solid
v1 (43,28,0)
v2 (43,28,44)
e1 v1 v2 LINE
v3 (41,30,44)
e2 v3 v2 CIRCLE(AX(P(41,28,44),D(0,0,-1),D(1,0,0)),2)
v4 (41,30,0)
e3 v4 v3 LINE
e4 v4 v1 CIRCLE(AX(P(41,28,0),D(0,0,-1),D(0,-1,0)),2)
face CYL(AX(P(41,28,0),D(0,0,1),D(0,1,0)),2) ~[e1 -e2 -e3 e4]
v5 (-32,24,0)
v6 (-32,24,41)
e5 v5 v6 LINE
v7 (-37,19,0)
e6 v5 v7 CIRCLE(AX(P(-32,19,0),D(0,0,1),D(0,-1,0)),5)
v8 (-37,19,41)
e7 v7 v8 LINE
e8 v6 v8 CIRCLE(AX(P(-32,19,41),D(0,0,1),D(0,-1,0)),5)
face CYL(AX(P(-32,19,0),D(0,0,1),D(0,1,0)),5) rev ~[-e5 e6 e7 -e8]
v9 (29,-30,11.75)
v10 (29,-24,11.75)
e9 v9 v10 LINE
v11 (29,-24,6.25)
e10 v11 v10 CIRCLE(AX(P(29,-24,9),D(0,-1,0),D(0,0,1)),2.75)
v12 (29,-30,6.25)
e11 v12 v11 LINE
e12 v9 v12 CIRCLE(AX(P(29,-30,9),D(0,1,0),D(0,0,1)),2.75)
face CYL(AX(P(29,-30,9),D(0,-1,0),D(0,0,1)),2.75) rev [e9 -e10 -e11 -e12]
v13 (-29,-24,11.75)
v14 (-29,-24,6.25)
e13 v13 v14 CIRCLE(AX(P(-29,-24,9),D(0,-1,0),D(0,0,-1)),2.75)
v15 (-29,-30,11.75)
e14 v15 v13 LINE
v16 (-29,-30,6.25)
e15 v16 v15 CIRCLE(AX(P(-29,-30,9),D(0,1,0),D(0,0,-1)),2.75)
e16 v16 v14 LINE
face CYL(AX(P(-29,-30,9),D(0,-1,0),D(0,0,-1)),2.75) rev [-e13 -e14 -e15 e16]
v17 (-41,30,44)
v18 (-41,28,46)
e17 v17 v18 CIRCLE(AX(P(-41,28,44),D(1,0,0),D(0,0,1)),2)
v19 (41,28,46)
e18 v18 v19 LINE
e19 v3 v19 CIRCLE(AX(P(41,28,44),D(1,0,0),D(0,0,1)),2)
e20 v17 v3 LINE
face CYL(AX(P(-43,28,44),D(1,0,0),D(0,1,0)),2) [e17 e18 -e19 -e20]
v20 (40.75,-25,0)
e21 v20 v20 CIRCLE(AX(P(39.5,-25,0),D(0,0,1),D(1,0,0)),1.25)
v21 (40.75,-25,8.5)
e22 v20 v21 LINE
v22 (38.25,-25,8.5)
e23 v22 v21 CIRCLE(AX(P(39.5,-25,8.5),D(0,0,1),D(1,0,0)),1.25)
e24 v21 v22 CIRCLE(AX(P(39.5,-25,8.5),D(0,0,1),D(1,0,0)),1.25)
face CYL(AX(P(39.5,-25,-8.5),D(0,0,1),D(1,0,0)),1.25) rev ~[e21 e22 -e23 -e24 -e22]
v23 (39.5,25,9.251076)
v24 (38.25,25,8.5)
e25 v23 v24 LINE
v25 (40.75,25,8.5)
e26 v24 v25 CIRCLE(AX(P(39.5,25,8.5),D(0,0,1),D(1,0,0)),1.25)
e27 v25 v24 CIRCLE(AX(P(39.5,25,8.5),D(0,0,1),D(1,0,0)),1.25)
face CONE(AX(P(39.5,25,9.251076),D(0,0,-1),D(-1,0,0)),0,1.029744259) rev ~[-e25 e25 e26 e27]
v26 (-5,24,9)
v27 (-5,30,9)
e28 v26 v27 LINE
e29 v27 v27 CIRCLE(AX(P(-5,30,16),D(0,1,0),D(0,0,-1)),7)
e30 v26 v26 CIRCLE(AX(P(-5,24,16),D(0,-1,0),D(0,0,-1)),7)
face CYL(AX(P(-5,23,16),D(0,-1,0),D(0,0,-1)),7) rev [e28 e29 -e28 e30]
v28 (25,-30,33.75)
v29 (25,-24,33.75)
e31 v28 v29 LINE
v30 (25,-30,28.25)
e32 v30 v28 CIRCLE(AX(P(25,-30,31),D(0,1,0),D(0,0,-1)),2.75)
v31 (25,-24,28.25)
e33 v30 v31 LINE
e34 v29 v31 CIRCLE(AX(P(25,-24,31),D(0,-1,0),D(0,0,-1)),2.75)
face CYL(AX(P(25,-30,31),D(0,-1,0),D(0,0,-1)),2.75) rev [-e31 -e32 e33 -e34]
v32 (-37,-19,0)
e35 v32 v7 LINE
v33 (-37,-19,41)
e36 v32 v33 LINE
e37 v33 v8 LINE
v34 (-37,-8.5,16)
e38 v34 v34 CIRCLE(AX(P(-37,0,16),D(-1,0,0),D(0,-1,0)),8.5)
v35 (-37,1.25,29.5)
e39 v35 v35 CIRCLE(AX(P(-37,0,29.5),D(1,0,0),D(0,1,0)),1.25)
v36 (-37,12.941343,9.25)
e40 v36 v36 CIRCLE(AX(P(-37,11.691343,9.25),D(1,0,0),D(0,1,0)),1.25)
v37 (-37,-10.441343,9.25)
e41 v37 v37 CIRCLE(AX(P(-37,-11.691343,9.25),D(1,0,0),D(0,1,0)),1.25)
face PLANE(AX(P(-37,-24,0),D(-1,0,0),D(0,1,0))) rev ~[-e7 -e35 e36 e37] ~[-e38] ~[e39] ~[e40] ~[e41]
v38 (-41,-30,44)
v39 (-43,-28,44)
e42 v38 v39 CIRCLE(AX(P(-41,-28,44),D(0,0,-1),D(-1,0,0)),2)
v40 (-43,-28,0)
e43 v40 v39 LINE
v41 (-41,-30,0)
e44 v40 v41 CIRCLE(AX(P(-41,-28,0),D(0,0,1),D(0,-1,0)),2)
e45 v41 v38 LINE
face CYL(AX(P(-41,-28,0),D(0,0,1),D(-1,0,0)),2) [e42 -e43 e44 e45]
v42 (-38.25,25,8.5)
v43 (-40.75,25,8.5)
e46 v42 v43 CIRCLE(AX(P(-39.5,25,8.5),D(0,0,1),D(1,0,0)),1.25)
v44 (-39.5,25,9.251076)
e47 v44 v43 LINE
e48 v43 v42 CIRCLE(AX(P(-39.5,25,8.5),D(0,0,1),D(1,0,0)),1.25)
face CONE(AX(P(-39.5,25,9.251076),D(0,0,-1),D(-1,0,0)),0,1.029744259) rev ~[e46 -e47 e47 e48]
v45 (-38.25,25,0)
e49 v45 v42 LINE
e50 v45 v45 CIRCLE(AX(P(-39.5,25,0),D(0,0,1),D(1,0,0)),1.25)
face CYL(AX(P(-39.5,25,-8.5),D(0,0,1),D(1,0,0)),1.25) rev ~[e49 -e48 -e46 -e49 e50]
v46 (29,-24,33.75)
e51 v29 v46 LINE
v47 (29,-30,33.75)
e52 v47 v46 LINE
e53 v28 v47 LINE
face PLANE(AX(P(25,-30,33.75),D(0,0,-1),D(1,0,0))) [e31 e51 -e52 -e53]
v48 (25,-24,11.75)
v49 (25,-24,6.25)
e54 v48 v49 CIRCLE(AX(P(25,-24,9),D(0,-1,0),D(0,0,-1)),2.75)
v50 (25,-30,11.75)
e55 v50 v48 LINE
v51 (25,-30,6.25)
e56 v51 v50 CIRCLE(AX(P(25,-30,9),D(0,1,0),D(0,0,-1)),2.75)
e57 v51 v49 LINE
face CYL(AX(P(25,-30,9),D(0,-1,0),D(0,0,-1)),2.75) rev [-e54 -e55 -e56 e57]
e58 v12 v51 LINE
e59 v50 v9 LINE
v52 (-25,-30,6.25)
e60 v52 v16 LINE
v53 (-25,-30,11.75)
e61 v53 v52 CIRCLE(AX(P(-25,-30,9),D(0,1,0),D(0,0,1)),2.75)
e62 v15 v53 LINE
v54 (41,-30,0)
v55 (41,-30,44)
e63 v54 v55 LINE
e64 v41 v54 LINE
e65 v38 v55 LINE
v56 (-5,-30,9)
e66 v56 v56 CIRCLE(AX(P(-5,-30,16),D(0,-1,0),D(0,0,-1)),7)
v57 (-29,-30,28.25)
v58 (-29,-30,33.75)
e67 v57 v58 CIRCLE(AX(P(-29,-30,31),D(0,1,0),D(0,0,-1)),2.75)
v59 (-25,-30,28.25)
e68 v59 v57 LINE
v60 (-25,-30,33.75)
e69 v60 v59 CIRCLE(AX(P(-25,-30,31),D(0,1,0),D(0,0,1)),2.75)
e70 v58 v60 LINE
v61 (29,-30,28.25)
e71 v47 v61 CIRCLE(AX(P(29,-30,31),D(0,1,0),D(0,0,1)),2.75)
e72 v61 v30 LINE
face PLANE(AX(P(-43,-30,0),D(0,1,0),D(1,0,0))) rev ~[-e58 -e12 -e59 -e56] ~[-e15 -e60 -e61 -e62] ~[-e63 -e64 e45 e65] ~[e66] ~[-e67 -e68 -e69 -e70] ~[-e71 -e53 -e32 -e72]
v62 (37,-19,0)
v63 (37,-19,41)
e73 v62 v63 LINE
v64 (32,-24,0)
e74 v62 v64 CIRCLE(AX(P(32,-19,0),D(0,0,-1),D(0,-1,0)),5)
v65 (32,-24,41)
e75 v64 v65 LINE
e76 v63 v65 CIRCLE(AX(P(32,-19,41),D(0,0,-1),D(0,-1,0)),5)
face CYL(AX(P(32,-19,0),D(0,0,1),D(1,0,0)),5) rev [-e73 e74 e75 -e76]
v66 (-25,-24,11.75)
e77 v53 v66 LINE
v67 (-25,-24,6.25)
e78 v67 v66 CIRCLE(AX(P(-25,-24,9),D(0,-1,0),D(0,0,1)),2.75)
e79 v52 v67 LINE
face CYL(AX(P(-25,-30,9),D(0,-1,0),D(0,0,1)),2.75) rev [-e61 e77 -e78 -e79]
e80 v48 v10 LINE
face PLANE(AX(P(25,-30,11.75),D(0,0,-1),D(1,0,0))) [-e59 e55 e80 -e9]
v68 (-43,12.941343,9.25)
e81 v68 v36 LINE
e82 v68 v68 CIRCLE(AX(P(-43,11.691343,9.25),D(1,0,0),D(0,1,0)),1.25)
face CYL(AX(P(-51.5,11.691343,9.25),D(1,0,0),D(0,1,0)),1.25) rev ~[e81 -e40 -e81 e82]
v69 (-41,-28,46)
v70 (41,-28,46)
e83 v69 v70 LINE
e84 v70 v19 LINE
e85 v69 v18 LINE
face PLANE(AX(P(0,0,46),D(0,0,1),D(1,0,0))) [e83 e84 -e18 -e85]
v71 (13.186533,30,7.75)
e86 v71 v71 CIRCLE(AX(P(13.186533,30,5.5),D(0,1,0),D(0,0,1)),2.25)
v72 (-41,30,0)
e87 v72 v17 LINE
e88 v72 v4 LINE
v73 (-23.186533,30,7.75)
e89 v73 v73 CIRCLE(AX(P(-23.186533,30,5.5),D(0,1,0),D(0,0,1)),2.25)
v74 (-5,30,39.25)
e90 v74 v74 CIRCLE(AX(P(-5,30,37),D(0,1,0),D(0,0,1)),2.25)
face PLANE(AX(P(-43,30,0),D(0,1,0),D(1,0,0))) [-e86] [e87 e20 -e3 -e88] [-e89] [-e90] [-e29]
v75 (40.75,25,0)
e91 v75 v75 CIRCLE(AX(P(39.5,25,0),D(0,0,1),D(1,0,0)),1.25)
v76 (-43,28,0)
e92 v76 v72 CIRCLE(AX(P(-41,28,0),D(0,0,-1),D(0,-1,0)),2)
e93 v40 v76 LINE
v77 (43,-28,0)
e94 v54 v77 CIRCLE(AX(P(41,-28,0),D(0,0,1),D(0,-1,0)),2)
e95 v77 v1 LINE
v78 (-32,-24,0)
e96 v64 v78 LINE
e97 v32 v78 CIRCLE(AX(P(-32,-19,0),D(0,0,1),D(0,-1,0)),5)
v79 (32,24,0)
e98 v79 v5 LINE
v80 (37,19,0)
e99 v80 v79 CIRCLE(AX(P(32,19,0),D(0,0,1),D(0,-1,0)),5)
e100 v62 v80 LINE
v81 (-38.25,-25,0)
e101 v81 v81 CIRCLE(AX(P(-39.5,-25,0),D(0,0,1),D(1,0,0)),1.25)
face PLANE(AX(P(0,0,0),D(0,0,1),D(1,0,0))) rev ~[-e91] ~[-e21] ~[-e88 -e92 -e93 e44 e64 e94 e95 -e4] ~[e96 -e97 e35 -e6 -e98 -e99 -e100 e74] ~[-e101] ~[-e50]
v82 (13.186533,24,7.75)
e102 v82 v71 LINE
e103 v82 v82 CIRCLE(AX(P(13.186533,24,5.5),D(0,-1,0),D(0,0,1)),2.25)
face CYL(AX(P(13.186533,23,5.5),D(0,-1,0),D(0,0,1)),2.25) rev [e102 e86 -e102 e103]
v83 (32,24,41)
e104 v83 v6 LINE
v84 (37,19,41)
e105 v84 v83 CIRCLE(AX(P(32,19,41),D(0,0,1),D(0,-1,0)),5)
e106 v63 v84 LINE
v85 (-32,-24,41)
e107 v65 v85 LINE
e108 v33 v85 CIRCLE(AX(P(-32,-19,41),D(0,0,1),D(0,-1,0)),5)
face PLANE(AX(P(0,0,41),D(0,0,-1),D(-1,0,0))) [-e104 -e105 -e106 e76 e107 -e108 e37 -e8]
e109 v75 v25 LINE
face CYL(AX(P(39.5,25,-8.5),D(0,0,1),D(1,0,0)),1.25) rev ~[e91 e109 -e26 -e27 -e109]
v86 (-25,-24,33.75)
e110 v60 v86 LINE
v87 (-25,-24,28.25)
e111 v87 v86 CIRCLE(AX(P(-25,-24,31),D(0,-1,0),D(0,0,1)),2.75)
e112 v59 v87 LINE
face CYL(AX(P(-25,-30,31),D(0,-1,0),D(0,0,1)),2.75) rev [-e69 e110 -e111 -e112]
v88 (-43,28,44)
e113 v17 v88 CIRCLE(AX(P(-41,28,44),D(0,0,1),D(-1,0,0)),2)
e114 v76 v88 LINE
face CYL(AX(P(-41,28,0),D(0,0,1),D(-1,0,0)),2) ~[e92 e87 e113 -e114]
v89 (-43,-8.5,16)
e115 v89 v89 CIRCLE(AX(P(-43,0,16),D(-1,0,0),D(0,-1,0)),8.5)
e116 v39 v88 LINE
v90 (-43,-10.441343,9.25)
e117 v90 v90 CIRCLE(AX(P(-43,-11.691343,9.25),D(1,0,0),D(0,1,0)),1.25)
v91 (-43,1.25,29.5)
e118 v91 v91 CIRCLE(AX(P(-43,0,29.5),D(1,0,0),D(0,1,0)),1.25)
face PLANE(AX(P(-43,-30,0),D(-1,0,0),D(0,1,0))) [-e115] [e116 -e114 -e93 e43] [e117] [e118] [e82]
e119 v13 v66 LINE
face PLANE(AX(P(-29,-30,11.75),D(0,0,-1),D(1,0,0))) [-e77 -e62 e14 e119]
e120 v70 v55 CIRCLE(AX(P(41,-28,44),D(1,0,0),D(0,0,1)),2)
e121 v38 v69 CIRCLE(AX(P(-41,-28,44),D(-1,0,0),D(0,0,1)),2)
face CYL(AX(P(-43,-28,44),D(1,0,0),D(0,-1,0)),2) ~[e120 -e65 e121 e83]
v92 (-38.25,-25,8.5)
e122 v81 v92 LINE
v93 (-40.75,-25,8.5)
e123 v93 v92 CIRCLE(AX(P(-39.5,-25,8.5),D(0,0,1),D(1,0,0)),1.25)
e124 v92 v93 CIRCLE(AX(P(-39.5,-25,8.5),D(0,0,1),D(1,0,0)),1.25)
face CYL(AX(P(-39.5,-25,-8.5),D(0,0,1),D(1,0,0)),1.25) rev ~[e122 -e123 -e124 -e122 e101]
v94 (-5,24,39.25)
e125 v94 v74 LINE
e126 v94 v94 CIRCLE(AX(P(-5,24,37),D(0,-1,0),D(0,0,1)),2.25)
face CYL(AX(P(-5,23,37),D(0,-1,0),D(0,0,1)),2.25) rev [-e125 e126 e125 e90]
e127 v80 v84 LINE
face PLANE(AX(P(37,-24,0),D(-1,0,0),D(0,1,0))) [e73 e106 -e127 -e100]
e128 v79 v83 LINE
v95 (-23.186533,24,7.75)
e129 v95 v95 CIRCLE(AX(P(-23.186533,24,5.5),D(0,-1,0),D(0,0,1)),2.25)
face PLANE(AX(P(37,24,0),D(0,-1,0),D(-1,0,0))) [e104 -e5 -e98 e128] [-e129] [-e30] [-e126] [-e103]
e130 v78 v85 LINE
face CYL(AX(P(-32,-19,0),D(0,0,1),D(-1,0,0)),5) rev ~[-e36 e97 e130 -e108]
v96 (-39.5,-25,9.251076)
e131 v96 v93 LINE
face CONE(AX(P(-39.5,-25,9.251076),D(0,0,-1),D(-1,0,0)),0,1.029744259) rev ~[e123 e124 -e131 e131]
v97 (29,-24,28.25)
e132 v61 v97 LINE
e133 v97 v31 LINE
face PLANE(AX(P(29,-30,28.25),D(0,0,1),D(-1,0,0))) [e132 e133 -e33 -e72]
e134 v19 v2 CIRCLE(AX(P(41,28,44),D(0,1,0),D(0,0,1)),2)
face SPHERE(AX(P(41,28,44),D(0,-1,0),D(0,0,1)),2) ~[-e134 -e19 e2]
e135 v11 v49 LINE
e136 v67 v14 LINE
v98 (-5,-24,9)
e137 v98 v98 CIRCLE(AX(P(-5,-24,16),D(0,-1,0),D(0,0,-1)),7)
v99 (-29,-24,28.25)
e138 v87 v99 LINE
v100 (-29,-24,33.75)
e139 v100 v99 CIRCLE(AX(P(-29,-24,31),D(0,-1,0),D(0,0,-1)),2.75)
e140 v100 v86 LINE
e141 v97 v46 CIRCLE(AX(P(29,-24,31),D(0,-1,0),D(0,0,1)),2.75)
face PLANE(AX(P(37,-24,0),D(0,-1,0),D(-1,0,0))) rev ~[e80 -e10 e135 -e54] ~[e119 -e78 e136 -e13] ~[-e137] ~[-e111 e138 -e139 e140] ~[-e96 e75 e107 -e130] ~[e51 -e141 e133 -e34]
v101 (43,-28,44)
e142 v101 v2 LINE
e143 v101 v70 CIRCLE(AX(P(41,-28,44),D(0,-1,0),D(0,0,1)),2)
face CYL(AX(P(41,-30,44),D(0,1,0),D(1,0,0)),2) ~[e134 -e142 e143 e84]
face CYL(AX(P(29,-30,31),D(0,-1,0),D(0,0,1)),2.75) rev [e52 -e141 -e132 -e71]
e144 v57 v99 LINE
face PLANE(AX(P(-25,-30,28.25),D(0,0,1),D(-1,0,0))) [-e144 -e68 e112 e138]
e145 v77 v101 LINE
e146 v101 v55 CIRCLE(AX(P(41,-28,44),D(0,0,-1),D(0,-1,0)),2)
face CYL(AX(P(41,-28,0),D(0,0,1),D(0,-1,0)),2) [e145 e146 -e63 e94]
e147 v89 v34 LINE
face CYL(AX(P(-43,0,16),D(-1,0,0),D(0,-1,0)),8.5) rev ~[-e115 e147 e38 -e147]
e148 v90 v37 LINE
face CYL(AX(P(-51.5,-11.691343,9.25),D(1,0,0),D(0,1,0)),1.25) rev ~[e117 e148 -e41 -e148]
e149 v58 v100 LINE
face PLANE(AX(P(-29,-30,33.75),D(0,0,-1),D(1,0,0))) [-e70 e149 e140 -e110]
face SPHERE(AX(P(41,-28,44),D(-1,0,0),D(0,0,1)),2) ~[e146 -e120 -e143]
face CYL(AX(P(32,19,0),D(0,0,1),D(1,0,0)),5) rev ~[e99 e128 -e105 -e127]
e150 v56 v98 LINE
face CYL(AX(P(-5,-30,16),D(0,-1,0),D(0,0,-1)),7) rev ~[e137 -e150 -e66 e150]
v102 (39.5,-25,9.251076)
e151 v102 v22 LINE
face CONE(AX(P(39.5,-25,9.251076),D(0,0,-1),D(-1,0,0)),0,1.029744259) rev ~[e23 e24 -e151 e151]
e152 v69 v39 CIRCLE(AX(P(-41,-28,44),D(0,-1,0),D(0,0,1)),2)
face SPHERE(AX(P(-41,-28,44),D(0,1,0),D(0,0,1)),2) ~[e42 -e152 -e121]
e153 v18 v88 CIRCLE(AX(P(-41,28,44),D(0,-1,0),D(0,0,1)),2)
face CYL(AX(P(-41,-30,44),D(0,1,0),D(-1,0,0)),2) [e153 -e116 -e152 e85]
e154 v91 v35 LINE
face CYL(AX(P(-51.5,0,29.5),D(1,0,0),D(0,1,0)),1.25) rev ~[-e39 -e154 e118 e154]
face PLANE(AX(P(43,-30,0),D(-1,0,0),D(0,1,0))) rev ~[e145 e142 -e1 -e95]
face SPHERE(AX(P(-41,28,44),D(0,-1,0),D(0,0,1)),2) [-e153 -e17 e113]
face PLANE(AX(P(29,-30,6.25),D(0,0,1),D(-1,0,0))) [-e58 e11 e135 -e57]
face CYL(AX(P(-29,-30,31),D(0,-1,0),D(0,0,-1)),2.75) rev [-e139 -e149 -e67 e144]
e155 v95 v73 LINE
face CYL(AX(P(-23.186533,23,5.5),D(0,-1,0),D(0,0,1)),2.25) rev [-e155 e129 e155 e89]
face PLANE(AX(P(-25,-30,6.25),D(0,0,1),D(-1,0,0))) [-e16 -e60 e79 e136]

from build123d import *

# Parameters (mm, degrees)
SKETCH_1_W             = 86
SKETCH_1_H             = 60
EXTRUDE_1_DEPTH        = 46
SKETCH_2_W             = 74
SKETCH_2_H             = 48
CUT_EXTRUDE_1_DEPTH    = 41
FILLET_1_R             = 5
SKETCH_3_R             = 7
CUT_EXTRUDE_3_DEPTH    = 7
CUT_EXTRUDE_START      = -7
SKETCH_4_R             = 7
SKETCH_4_R_2           = 2.25
CUT_EXTRUDE_4_DEPTH    = 7
SKETCH_5_R             = 8.5
CUT_EXTRUDE_5_DEPTH    = 7
HOLE_WIZARD_M3_2_D     = 2.5
HOLE_WIZARD_M3_2_DEPTH = 8.5
HOLE_WIZARD_M3_2_TIP   = 0.751075774
HOLE_WIZARD_M3_3_D     = 2.5
HOLE_WIZARD_M3_3_DEPTH = 8.5
HOLE_WIZARD_M3_3_TIP   = 0.751075774
FILLET_2_R             = 2


with BuildPart() as part:
    # 草图1 → 凸台-拉伸1 (new body)
    with BuildSketch(Plane.XY):
        Rectangle(SKETCH_1_W, SKETCH_1_H)
    extrude(amount=EXTRUDE_1_DEPTH)

    # 草图2 → 切除-拉伸1 (cut)
    with BuildSketch(Plane(origin=(0, 0, 0), x_dir=(-1, 0, 0), z_dir=(0, 0, -1))):
        Rectangle(SKETCH_2_W, SKETCH_2_H)
    extrude(amount=-CUT_EXTRUDE_1_DEPTH, mode=Mode.SUBTRACT)

    # 圆角1
    fillet_1_edges = [part.edges().sort_by_distance(p)[0] for p in [
        (-37, -24, 20.5),
        (37, -24, 20.5),
        (37, 24, 20.5),
        (-37, 24, 20.5),
    ]]
    fillet(fillet_1_edges, radius=FILLET_1_R)

    # 草图3 → 切除-拉伸3 (cut)
    with BuildSketch(Plane.XZ.offset(30)):
        with Locations(Location((-5, 16, 0), (0, 0, 270))):
            Circle(SKETCH_3_R)
        with BuildLine():
            Line((25, 11.75), (29, 11.75))
            ThreePointArc((29, 11.75), (31.75, 9), (29, 6.25))
            Line((29, 6.25), (25, 6.25))
            ThreePointArc((25, 6.25), (22.25, 9), (25, 11.75))
        make_face()
        with BuildLine():
            Line((25, 33.75), (29, 33.75))
            ThreePointArc((29, 33.75), (31.75, 31), (29, 28.25))
            Line((29, 28.25), (25, 28.25))
            ThreePointArc((25, 28.25), (22.25, 31), (25, 33.75))
        make_face()
        with BuildLine():
            Line((-29, 33.75), (-25, 33.75))
            ThreePointArc((-25, 33.75), (-22.25, 31), (-25, 28.25))
            Line((-25, 28.25), (-29, 28.25))
            ThreePointArc((-29, 28.25), (-31.75, 31), (-29, 33.75))
        make_face()
        with BuildLine():
            Line((-29, 11.75), (-25, 11.75))
            ThreePointArc((-25, 11.75), (-22.25, 9), (-25, 6.25))
            Line((-25, 6.25), (-29, 6.25))
            ThreePointArc((-29, 6.25), (-31.75, 9), (-29, 11.75))
        make_face()
    extrude(amount=-CUT_EXTRUDE_3_DEPTH, mode=Mode.SUBTRACT)

    # 草图4 → 切除-拉伸4 (cut)
    with BuildSketch(Plane(origin=(0, 30, 0), x_dir=(1, 0, 0), z_dir=(0, 1, 0)).offset(CUT_EXTRUDE_START)):
        with Locations(Location((-5, -16, 0), (0, 0, 90))):
            Circle(SKETCH_4_R)
        with Locations(Location((13.186533479, -5.5, 0), (0, 0, 270))):
            Circle(SKETCH_4_R_2)
        with Locations(Location((-5, -37, 0), (0, 0, 270))):
            Circle(SKETCH_4_R_2)
        with Locations(Location((-23.186533479, -5.5, 0), (0, 0, 270))):
            Circle(SKETCH_4_R_2)
    extrude(amount=CUT_EXTRUDE_4_DEPTH, mode=Mode.SUBTRACT)

    # 草图5 → 切除-拉伸5 (cut)
    with BuildSketch(Plane.ZY.offset(43)):
        with Locations(Location((16, 0, 0), (0, 0, 270))):
            Circle(SKETCH_5_R)
    extrude(amount=-CUT_EXTRUDE_5_DEPTH, mode=Mode.SUBTRACT)

    # M3 螺纹孔2
    with Locations(Plane(origin=(-43, 0, 29.5), x_dir=(0, -1, 0), z_dir=(-1, 0, 0))):
        with Locations((0, 0), (11.691342951, -20.25), (-11.691342951, -20.25)):
            Hole(HOLE_WIZARD_M3_2_D / 2, depth=HOLE_WIZARD_M3_2_DEPTH)
            with Locations((0, 0, -(HOLE_WIZARD_M3_2_DEPTH + HOLE_WIZARD_M3_2_TIP / 2))):  # 118° drill point
                Cone(0, HOLE_WIZARD_M3_2_D / 2, HOLE_WIZARD_M3_2_TIP, mode=Mode.SUBTRACT)

    # M3 螺纹孔3
    with Locations(Plane(origin=(39.5, 25, 0), x_dir=(-1, 0, 0), z_dir=(0, 0, -1))):
        with Locations((0, 0), (79, 0), (79, -50), (0, -50)):
            Hole(HOLE_WIZARD_M3_3_D / 2, depth=HOLE_WIZARD_M3_3_DEPTH)
            with Locations((0, 0, -(HOLE_WIZARD_M3_3_DEPTH + HOLE_WIZARD_M3_3_TIP / 2))):  # 118° drill point
                Cone(0, HOLE_WIZARD_M3_3_D / 2, HOLE_WIZARD_M3_3_TIP, mode=Mode.SUBTRACT)

    # 圆角2
    fillet_2_edges = [part.edges().sort_by_distance(p)[0] for p in [
        (-43, 0, 46),
        (0, -30, 46),
        (43, 0, 46),
        (0, 30, 46),
        (43, -30, 23),
        (-43, -30, 23),
        (-43, 30, 23),
        (43, 30, 23),
    ]]
    fillet(fillet_2_edges, radius=FILLET_2_R)


solid = part.part
